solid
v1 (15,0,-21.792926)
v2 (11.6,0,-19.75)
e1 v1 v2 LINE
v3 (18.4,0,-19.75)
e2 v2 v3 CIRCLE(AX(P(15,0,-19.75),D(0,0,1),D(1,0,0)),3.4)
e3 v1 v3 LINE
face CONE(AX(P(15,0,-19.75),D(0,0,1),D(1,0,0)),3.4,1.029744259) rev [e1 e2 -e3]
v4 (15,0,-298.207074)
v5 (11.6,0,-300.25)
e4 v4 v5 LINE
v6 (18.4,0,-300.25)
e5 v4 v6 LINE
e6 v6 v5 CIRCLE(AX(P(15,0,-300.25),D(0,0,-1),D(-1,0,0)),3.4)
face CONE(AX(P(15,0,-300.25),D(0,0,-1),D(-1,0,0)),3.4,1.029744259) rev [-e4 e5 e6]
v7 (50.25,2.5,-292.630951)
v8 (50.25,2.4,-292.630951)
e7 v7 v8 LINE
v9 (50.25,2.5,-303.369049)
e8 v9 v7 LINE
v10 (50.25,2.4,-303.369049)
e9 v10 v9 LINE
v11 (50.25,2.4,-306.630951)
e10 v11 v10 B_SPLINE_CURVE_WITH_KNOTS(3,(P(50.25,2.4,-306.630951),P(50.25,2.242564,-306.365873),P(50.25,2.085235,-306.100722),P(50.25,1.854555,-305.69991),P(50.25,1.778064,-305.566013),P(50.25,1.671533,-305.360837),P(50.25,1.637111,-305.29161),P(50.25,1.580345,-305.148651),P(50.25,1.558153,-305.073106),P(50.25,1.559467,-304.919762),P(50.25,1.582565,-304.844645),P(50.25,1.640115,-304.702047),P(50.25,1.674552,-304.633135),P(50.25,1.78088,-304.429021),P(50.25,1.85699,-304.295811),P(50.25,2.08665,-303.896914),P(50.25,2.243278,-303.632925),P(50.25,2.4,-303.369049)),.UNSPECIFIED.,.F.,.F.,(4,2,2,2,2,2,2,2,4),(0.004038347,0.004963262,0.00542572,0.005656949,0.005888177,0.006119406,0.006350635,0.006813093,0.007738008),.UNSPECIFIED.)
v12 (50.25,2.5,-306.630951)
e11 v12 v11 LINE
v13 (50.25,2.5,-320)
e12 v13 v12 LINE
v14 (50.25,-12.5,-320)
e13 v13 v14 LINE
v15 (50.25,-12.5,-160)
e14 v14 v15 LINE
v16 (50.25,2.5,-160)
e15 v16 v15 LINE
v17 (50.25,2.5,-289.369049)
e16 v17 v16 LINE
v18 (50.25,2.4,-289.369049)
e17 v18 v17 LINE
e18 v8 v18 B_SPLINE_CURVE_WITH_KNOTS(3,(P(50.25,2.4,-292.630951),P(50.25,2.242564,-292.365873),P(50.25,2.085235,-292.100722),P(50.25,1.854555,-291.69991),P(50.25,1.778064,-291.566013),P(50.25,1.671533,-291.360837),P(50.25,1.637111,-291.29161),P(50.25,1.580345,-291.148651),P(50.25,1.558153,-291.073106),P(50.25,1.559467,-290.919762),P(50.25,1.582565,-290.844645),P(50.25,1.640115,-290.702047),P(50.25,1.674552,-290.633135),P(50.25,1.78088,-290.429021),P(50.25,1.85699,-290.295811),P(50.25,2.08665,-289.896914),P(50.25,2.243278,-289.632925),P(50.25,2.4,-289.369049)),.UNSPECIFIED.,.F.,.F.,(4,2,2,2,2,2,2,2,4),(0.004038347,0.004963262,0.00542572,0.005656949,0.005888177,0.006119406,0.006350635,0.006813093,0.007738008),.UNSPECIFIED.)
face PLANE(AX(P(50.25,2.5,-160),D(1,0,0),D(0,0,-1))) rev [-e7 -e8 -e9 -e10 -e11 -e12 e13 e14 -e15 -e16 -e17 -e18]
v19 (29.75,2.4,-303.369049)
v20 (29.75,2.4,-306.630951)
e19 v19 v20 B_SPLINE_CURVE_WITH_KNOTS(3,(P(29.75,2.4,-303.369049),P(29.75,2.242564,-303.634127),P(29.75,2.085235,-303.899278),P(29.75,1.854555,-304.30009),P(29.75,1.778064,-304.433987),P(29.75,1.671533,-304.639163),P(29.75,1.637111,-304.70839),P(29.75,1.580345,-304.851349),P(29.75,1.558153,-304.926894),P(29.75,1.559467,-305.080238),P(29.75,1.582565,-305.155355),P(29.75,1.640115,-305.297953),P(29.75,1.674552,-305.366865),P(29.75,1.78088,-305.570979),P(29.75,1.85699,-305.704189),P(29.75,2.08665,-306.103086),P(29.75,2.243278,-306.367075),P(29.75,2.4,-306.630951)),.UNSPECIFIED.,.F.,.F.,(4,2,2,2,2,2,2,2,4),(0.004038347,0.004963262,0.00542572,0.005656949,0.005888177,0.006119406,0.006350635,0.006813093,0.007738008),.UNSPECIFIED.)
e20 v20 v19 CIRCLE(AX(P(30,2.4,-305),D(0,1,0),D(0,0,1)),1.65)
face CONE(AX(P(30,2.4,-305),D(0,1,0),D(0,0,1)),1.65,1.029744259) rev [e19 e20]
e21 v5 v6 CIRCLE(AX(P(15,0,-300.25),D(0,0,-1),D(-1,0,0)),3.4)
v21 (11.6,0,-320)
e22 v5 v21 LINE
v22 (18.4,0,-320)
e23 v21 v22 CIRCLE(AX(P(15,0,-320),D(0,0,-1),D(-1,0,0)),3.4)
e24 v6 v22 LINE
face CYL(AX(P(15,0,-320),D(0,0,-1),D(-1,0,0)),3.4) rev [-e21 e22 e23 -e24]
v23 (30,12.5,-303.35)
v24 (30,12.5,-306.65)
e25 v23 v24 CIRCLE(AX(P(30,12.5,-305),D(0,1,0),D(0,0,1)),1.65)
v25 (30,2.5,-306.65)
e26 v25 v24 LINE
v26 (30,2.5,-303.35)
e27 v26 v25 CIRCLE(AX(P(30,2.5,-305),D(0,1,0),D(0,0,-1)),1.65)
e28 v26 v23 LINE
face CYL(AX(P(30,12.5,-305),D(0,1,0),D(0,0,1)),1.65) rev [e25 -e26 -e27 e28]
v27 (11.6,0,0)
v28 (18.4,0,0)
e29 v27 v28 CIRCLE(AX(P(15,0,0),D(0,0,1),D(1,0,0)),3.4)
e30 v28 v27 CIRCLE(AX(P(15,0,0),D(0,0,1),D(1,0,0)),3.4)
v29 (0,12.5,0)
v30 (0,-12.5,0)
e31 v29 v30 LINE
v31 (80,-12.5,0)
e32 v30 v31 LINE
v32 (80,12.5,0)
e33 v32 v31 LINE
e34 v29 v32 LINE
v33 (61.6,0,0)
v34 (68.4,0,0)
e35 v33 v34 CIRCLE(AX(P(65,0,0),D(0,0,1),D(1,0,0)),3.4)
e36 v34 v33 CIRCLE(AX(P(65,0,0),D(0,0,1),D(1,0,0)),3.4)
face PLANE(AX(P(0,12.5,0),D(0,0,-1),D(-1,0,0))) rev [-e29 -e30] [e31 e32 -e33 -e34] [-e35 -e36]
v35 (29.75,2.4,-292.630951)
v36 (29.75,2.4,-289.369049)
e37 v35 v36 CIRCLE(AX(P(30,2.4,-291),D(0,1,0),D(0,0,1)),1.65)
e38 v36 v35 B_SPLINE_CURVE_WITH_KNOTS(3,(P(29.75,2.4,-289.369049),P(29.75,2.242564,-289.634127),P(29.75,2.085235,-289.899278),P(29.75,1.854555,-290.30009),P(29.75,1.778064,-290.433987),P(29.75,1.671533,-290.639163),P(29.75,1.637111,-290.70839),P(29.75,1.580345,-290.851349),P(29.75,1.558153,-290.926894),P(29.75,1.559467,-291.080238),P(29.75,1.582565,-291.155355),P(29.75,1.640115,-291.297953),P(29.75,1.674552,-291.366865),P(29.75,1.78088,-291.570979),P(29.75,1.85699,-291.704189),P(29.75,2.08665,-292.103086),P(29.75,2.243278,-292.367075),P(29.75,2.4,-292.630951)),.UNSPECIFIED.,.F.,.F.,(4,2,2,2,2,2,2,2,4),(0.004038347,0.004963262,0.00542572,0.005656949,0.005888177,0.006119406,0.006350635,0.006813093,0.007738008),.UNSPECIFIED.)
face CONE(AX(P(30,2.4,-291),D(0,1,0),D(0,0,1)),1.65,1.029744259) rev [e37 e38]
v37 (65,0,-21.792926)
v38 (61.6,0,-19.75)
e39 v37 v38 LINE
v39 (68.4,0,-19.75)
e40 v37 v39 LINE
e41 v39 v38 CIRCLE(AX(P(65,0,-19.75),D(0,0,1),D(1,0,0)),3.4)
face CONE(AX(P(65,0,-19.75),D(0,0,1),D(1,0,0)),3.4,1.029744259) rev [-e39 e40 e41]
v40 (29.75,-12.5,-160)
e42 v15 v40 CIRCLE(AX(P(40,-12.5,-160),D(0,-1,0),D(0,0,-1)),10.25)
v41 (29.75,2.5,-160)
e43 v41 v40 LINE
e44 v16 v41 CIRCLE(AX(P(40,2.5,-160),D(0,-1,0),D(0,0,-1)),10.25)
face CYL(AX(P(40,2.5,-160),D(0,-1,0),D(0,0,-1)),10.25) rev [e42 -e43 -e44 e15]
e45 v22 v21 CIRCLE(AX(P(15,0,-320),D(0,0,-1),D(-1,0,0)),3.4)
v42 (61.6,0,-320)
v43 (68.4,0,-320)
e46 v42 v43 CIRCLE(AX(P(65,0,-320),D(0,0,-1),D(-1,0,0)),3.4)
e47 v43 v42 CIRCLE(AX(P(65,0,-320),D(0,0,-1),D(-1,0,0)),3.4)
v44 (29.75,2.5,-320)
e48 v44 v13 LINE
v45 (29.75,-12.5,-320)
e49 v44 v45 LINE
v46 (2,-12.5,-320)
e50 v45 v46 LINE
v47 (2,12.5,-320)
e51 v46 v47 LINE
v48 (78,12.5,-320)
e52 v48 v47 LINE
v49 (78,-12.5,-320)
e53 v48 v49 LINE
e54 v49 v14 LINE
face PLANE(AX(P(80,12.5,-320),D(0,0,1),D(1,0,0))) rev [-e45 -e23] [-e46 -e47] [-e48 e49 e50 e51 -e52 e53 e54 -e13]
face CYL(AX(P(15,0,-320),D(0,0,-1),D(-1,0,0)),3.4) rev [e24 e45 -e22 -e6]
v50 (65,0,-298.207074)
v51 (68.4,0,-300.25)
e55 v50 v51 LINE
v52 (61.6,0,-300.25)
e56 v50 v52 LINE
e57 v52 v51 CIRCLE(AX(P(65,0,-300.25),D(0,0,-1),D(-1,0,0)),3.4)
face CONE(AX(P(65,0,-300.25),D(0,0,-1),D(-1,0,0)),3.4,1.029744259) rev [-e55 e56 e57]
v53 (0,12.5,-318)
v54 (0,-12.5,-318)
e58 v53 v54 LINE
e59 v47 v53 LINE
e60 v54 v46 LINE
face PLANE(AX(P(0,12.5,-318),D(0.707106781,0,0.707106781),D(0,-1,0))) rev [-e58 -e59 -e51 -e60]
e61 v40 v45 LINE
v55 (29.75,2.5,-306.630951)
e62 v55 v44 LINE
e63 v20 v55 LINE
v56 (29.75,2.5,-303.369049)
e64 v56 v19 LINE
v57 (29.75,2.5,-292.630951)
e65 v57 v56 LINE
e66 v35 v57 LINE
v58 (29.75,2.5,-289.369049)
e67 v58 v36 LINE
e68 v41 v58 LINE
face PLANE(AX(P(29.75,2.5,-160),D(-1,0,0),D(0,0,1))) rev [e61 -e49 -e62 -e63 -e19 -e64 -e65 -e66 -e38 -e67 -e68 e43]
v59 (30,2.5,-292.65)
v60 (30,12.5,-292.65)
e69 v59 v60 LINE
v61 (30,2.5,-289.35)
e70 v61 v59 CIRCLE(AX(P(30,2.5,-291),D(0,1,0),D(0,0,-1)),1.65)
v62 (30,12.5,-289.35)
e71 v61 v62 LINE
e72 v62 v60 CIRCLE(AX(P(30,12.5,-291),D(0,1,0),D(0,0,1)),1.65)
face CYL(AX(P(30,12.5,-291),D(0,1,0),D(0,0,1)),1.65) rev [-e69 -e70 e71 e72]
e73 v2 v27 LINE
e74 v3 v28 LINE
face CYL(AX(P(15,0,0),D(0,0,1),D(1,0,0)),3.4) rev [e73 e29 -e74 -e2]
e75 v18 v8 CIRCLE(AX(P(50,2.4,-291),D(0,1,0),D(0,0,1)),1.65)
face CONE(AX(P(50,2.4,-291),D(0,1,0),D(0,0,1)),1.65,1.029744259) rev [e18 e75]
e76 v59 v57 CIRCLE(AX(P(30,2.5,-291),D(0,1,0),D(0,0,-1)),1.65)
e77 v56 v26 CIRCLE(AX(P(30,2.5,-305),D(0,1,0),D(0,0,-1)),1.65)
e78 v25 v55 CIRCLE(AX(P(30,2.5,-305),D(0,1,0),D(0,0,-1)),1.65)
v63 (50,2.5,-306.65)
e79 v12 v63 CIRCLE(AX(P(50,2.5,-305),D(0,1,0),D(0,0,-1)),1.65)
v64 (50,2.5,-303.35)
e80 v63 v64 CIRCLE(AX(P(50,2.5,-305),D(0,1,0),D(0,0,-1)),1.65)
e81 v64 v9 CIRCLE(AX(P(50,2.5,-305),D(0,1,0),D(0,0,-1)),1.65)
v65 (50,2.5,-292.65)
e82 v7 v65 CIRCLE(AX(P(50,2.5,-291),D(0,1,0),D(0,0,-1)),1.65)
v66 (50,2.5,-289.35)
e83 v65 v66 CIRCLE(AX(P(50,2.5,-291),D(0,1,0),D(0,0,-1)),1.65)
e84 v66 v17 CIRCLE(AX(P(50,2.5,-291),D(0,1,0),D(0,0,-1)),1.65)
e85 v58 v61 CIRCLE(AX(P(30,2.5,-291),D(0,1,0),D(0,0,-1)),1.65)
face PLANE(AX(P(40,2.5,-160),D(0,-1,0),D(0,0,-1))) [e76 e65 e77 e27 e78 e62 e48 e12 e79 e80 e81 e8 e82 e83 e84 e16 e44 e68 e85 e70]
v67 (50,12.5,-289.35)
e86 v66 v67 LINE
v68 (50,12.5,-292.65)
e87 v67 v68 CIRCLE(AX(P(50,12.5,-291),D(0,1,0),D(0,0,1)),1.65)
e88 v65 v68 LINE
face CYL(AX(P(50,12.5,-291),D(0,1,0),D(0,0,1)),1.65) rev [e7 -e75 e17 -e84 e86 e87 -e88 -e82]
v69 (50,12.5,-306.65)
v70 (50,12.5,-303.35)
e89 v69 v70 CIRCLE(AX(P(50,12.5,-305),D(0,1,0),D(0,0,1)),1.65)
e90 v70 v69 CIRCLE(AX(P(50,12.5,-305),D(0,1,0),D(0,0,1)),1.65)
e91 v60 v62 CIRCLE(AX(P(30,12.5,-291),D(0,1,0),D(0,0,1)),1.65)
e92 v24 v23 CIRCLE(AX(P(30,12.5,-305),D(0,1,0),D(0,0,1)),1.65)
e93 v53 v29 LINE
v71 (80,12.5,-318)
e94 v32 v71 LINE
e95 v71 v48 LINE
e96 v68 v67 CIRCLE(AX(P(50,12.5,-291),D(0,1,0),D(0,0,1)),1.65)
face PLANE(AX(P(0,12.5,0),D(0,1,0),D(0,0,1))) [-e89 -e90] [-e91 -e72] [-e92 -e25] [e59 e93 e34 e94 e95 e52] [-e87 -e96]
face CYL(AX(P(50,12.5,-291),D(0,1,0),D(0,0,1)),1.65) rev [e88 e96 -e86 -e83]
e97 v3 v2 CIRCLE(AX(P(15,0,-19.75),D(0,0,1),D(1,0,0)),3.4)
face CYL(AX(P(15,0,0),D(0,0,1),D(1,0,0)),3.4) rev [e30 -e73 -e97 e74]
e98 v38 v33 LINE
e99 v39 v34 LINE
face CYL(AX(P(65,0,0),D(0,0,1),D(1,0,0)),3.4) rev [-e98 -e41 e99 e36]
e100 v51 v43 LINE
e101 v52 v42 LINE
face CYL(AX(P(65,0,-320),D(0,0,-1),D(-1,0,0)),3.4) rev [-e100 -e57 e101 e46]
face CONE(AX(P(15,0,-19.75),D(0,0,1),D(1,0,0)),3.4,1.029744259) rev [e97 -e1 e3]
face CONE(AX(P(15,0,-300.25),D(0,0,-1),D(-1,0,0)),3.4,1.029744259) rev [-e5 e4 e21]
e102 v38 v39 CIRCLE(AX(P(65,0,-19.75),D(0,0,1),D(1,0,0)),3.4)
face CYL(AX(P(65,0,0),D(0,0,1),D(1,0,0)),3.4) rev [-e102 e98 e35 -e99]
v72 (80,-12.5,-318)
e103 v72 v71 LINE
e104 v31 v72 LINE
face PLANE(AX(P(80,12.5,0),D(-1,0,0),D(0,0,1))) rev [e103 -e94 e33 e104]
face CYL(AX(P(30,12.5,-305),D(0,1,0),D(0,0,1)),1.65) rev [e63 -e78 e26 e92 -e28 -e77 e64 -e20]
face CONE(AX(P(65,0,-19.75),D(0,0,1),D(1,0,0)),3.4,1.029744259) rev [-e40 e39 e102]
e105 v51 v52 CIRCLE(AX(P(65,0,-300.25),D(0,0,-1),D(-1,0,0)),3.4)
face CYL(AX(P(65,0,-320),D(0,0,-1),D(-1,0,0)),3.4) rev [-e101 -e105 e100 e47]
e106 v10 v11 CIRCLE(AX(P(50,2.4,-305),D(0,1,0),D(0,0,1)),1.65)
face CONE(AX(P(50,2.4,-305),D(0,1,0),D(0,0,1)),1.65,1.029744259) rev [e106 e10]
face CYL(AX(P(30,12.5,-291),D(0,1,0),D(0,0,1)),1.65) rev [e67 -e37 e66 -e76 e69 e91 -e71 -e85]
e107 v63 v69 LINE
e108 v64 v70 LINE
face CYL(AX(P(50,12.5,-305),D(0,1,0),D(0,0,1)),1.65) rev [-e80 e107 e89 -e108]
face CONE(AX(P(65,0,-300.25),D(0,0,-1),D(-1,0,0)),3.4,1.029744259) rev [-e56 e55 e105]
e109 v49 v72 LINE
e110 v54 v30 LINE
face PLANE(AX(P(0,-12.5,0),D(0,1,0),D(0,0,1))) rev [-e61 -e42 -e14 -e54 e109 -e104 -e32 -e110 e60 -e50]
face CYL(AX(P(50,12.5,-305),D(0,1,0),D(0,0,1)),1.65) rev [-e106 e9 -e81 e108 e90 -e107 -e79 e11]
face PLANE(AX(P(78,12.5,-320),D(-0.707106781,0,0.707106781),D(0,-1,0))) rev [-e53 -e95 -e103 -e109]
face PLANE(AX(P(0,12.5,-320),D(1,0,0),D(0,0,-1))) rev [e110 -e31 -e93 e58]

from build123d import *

# Parameters (mm, degrees)
SKETCH1_W             = 80
SKETCH1_H             = 320
BOSS_EXTRUDE1_DEPTH   = 12.5
M8_TAPPED_HOLE1_D     = 6.8
M8_TAPPED_HOLE1_DEPTH = 19.75
M8_TAPPED_HOLE1_TIP   = 2.042926105
CHAMFER1_SIZE         = 2
M4_TAPPED_HOLE1_D     = 3.3
M4_TAPPED_HOLE1_DEPTH = 10.1
M4_TAPPED_HOLE1_TIP   = 0.991420021
M8_TAPPED_HOLE2_D     = 6.8
M8_TAPPED_HOLE2_DEPTH = 19.75
M8_TAPPED_HOLE2_TIP   = 2.042926105
CUT_EXTRUDE2_DEPTH    = 15


with BuildPart() as part:
    # Sketch1 → Boss-Extrude1 (new, symmetric)
    with BuildSketch(Plane(origin=(0, 0, 0), x_dir=(1, 0, 0), z_dir=(0, 1, 0))):
        with Locations((40, 160)):
            Rectangle(SKETCH1_W, SKETCH1_H)
    extrude(amount=BOSS_EXTRUDE1_DEPTH, both=True)

    # M8 Tapped Hole1
    with Locations(Plane.XY):
        with Locations((15, 0), (65, 0)):
            Hole(M8_TAPPED_HOLE1_D / 2, depth=M8_TAPPED_HOLE1_DEPTH)
            with Locations((0, 0, -(M8_TAPPED_HOLE1_DEPTH + M8_TAPPED_HOLE1_TIP / 2))):  # 118° drill point
                Cone(0, M8_TAPPED_HOLE1_D / 2, M8_TAPPED_HOLE1_TIP, mode=Mode.SUBTRACT)

    # Chamfer1
    chamfer1_edges = [part.edges().sort_by_distance(p)[0] for p in [
        (0, 0, -320),
        (80, 0, -320),
    ]]
    chamfer(chamfer1_edges, length=CHAMFER1_SIZE)

    # M4 Tapped Hole1
    with Locations(Plane(origin=(0, 12.5, 0), x_dir=(1, 0, 0), z_dir=(0, 1, 0))):
        with Locations((30, 305), (30, 291), (50, 291), (50, 305)):
            Hole(M4_TAPPED_HOLE1_D / 2, depth=M4_TAPPED_HOLE1_DEPTH)
            with Locations((0, 0, -(M4_TAPPED_HOLE1_DEPTH + M4_TAPPED_HOLE1_TIP / 2))):  # 118° drill point
                Cone(0, M4_TAPPED_HOLE1_D / 2, M4_TAPPED_HOLE1_TIP, mode=Mode.SUBTRACT)

    # M8 Tapped Hole2
    with Locations(Plane(origin=(0, 0, -320), x_dir=(-1, 0, 0), z_dir=(0, 0, -1))):
        with Locations((-15, 0), (-65, 0)):
            Hole(M8_TAPPED_HOLE2_D / 2, depth=M8_TAPPED_HOLE2_DEPTH)
            with Locations((0, 0, -(M8_TAPPED_HOLE2_DEPTH + M8_TAPPED_HOLE2_TIP / 2))):  # 118° drill point
                Cone(0, M8_TAPPED_HOLE2_D / 2, M8_TAPPED_HOLE2_TIP, mode=Mode.SUBTRACT)

    # Sketch11 → Cut-Extrude2 (cut)
    with BuildSketch(Plane.XZ.offset(12.5)):
        with BuildLine():
            Line((50.25, -160), (50.25, -320))
            ThreePointArc((50.25, -320), (40, -330.25), (29.75, -320))
            Line((29.75, -320), (29.75, -160))
            ThreePointArc((29.75, -160), (40, -149.75), (50.25, -160))
        make_face()
    extrude(amount=-CUT_EXTRUDE2_DEPTH, mode=Mode.SUBTRACT)


solid = part.part
